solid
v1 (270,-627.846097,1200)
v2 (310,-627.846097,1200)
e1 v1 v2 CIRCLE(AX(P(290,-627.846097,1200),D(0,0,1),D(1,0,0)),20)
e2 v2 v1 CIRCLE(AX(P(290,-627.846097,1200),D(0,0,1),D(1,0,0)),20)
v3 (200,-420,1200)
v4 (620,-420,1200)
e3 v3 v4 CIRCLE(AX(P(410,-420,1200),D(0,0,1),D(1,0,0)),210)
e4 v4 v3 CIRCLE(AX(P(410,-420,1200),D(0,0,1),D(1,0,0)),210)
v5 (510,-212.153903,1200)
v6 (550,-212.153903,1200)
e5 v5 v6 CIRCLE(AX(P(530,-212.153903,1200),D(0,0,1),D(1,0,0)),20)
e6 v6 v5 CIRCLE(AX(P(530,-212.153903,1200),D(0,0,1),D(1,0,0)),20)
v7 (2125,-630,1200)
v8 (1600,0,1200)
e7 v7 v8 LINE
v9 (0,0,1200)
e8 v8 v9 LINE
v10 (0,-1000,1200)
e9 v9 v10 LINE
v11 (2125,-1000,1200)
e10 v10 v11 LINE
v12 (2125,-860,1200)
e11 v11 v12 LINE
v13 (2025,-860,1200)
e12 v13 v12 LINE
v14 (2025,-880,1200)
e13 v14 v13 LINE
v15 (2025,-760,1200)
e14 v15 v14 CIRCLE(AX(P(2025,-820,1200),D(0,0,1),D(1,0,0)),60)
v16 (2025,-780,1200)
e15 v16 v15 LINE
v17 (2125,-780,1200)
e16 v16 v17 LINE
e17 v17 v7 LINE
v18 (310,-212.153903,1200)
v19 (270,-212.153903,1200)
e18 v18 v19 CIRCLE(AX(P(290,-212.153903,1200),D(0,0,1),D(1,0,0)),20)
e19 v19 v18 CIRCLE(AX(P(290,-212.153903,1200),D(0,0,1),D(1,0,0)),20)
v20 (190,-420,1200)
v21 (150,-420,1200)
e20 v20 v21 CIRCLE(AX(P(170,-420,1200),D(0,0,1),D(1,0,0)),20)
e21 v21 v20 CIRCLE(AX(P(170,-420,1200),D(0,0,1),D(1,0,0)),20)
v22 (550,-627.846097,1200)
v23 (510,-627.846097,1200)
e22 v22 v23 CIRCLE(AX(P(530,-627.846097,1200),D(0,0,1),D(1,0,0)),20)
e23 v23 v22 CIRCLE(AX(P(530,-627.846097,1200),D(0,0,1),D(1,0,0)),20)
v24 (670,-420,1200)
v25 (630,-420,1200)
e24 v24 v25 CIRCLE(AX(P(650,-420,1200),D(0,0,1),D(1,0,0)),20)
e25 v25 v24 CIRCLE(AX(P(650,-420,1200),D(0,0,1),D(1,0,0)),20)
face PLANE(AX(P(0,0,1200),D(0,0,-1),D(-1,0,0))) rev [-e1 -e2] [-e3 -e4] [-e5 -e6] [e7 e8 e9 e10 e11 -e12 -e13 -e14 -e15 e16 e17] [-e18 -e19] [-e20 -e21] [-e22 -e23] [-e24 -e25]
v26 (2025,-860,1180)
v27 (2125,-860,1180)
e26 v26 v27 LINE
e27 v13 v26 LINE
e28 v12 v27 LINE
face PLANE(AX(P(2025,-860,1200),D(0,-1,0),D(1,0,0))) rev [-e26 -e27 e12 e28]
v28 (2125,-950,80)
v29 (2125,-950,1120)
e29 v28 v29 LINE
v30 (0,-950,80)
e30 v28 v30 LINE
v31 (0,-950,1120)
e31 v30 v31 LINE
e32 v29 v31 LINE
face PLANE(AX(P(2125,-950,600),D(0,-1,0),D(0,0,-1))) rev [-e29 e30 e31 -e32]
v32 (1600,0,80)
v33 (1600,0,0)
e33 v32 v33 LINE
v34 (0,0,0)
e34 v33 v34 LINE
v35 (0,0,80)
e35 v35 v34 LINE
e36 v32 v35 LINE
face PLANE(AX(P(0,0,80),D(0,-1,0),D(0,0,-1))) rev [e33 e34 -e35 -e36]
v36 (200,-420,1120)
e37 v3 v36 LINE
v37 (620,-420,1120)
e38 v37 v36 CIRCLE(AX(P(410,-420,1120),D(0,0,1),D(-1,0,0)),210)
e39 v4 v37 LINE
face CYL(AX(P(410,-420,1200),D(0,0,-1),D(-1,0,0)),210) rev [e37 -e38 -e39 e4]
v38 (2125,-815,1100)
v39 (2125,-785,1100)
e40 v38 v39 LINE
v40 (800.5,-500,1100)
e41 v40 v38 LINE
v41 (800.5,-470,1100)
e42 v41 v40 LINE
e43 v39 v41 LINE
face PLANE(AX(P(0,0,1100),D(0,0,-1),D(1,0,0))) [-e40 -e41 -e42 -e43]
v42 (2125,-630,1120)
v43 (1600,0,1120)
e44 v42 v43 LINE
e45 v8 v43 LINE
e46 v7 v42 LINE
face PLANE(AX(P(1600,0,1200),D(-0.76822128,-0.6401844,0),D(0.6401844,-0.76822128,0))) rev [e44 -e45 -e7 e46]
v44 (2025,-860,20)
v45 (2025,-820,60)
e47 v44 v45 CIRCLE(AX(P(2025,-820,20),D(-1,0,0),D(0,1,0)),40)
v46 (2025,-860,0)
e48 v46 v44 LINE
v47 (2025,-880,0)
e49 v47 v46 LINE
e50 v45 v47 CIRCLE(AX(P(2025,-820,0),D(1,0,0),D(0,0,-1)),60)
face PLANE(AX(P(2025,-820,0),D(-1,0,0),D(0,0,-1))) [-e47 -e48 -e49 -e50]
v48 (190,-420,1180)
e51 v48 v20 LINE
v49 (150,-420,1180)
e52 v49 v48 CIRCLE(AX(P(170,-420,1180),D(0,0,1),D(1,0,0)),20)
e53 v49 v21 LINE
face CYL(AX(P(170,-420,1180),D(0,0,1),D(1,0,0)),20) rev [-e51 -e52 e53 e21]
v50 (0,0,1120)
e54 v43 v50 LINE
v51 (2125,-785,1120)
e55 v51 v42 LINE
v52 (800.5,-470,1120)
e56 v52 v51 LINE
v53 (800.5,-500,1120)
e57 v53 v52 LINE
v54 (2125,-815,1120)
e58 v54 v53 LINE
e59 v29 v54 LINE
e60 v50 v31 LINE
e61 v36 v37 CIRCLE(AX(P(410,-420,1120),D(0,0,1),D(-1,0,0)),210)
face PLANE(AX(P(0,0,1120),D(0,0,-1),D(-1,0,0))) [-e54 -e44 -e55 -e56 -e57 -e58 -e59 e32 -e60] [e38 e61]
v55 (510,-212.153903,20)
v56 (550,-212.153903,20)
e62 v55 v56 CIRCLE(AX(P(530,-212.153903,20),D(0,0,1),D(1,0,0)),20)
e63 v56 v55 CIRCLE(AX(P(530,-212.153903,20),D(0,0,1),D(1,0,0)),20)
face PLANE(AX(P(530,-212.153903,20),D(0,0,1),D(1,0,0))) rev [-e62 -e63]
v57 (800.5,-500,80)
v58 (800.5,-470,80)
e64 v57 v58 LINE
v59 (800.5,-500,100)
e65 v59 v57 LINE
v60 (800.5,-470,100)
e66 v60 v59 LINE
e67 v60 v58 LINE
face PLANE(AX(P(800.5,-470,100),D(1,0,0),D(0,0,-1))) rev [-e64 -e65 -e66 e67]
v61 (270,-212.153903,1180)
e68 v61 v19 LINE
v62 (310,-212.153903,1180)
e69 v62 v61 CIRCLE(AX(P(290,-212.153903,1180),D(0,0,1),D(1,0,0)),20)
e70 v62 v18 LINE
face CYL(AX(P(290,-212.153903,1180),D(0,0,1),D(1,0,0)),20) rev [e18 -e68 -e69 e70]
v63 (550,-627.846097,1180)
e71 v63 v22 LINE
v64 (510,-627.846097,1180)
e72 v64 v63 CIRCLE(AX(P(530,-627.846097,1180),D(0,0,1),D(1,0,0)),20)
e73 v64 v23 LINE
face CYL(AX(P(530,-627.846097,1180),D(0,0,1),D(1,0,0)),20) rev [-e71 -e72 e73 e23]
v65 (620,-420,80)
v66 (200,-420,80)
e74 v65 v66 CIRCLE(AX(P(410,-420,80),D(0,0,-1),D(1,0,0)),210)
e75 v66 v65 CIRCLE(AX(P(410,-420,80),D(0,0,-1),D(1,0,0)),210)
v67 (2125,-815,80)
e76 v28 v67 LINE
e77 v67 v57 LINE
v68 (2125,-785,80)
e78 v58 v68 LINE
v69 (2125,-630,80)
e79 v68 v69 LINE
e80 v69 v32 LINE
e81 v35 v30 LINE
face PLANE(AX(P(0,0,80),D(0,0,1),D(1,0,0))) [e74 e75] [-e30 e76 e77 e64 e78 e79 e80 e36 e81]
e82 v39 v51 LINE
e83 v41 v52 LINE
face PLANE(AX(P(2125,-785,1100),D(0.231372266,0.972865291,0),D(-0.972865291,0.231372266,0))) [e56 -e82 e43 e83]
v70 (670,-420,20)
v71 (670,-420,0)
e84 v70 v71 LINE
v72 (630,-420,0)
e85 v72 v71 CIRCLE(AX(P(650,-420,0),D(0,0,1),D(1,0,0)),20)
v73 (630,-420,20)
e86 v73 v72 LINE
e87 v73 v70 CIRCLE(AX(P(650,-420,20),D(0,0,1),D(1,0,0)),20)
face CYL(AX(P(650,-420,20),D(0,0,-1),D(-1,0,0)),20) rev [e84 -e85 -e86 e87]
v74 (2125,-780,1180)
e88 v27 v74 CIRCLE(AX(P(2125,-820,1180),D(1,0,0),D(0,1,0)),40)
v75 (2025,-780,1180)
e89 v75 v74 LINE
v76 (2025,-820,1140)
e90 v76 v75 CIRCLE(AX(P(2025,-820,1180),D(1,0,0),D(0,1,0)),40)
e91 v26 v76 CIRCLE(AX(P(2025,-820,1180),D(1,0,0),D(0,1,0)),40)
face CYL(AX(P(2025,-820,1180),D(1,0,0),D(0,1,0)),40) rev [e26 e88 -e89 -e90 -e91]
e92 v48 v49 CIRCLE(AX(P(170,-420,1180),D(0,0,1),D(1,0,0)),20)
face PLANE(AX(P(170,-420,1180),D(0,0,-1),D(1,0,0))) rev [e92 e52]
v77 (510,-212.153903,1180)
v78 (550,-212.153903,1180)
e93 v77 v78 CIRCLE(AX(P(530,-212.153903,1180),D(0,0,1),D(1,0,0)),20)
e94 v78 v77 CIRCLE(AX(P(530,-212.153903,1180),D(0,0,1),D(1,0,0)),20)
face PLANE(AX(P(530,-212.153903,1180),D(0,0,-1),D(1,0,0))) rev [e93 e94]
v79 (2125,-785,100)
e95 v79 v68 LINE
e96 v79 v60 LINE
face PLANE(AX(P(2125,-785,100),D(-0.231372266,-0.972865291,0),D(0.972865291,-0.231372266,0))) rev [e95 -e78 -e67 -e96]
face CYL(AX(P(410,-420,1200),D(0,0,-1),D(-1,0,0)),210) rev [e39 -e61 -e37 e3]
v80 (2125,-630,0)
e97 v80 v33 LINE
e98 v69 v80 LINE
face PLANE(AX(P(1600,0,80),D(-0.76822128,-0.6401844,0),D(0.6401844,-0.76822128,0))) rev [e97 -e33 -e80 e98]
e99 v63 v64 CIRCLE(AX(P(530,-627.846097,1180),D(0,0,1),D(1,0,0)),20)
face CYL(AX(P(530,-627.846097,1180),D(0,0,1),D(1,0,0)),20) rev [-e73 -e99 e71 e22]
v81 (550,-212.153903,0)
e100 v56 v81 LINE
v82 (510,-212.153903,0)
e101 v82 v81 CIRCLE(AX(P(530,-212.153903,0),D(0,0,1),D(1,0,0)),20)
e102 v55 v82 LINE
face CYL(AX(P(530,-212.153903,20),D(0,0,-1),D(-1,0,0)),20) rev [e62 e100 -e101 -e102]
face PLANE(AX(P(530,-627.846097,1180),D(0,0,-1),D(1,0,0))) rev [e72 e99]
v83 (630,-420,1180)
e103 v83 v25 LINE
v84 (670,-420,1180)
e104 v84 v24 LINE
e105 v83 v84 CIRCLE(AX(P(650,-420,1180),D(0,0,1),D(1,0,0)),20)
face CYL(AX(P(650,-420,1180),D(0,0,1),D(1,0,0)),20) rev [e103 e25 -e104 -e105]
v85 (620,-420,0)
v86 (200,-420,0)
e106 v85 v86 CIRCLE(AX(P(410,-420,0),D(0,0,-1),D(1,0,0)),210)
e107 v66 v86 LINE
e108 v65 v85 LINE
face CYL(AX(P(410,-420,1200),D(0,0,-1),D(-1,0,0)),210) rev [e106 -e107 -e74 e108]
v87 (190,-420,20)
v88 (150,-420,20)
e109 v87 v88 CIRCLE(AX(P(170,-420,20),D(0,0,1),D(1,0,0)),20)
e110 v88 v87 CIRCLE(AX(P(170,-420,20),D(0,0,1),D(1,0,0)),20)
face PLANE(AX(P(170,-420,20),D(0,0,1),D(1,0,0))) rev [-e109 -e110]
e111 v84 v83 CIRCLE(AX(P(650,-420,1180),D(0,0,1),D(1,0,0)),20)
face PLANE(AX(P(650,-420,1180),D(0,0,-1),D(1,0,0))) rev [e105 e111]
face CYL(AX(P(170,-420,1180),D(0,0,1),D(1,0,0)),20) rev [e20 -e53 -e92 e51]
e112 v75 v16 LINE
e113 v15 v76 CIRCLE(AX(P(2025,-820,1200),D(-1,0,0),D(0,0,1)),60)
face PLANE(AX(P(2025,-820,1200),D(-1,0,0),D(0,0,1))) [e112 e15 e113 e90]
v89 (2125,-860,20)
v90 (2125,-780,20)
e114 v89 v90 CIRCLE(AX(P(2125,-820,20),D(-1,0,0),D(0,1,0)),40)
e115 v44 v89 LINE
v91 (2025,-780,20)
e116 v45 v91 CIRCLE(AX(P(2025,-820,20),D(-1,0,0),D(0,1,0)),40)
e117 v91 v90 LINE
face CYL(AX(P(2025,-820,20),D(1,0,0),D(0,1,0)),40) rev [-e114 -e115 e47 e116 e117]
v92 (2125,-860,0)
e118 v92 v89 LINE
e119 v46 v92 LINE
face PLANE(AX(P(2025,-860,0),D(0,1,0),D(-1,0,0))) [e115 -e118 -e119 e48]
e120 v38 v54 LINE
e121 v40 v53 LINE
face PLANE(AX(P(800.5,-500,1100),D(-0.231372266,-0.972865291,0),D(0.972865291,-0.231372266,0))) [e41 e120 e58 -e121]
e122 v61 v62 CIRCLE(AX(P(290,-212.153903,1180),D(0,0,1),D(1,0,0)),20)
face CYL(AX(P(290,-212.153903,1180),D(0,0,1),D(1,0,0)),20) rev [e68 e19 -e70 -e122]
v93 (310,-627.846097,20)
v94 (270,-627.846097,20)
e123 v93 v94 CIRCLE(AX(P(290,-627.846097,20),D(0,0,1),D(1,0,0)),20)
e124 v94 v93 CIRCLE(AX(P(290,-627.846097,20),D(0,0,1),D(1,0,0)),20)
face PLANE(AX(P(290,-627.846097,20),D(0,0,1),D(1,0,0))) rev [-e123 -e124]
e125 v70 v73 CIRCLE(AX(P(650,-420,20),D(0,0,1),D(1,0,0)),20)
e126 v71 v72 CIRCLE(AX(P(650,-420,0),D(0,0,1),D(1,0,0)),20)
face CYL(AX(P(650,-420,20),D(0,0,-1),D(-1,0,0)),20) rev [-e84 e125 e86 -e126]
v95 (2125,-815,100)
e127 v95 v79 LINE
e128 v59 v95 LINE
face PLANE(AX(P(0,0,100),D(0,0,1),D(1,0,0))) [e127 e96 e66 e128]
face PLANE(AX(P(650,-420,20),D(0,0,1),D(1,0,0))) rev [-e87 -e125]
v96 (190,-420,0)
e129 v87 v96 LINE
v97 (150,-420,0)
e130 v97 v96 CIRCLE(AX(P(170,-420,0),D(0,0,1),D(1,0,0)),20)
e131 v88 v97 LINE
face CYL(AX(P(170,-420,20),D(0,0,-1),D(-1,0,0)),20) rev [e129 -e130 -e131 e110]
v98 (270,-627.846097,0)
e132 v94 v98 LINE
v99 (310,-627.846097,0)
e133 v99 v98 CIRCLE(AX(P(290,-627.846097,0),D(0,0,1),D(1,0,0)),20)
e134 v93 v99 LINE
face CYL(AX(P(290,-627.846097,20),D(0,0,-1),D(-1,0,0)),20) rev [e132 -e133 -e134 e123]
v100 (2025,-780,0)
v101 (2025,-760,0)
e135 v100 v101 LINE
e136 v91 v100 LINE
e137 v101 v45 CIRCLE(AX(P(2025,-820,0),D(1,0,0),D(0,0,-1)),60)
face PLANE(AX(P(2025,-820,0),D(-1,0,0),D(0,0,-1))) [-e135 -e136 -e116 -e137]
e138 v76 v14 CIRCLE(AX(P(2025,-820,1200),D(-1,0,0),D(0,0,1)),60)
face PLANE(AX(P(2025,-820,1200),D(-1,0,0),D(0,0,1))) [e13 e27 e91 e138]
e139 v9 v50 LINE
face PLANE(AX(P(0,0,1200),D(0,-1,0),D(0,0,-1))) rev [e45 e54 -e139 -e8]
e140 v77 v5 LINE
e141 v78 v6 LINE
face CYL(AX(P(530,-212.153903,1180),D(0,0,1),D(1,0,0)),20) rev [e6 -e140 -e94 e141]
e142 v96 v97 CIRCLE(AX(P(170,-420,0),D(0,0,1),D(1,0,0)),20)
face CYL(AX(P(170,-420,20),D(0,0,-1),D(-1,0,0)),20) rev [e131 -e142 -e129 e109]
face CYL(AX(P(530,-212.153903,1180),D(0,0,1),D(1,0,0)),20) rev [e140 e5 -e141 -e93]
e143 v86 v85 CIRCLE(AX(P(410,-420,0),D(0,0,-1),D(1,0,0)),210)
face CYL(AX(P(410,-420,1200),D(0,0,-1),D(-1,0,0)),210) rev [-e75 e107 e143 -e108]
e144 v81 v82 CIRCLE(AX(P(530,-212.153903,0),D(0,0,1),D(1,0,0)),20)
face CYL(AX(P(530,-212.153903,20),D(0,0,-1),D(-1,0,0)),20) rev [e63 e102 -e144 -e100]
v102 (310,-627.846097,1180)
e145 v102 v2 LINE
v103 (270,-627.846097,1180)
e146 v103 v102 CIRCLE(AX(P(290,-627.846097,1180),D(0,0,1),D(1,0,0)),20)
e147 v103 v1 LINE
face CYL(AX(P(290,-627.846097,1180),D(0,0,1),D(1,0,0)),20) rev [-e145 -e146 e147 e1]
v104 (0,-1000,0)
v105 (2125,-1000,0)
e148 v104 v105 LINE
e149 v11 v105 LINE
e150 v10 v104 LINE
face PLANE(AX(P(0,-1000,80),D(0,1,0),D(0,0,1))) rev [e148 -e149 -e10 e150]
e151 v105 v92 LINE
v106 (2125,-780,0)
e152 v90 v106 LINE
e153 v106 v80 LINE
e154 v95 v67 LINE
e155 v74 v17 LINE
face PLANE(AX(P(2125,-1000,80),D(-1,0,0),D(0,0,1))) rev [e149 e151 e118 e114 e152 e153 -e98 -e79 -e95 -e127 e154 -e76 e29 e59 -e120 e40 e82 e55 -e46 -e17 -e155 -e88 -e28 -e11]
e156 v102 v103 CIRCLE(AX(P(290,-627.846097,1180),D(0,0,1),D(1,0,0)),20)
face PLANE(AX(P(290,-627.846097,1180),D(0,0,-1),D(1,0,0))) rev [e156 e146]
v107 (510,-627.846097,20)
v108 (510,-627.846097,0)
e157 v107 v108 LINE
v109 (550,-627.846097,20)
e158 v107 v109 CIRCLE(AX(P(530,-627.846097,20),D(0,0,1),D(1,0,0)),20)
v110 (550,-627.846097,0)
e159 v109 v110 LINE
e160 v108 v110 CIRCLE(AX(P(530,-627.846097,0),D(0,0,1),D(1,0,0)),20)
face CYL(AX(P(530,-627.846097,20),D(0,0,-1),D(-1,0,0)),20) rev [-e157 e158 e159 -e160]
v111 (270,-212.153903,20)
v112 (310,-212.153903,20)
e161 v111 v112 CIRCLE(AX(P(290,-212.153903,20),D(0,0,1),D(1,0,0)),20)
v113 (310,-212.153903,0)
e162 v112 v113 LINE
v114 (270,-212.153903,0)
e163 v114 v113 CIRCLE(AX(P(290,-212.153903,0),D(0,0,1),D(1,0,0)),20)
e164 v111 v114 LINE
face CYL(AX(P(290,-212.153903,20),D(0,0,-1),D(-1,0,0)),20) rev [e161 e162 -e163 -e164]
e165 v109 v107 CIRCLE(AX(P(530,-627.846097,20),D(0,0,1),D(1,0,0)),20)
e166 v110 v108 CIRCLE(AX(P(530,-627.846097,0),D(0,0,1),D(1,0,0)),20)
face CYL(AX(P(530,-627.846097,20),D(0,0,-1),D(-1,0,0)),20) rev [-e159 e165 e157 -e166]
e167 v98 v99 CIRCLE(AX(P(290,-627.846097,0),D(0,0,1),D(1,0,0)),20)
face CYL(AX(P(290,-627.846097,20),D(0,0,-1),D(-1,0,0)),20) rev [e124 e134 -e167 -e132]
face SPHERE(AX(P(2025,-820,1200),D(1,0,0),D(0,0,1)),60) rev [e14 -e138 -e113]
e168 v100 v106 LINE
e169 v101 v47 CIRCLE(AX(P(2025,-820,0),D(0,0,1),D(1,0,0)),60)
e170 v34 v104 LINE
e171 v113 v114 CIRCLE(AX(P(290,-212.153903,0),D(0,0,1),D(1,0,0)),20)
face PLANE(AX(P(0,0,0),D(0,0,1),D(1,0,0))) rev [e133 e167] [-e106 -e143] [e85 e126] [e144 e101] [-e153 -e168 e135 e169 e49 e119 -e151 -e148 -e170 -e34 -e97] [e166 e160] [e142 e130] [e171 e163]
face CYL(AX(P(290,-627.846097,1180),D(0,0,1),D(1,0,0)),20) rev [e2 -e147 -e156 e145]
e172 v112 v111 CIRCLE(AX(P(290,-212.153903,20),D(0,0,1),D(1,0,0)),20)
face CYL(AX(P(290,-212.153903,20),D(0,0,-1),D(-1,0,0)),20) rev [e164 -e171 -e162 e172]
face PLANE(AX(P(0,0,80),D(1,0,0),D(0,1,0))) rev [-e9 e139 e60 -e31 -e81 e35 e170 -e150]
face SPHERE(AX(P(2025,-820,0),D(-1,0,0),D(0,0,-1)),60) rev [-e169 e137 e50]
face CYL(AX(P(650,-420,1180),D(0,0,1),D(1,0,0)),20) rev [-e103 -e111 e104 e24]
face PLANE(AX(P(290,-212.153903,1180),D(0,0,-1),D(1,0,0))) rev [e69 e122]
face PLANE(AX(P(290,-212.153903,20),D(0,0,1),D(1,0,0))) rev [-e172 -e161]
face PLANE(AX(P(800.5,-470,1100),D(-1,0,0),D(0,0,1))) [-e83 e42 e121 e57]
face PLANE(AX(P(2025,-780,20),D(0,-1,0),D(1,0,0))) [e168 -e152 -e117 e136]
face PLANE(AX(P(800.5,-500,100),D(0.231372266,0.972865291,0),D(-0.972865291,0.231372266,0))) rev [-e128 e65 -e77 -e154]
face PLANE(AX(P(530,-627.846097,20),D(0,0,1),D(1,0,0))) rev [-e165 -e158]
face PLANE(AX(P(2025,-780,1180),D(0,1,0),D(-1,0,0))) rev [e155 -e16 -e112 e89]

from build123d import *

# Parameters (mm, degrees)
EXTRUDE_1_DEPTH          = 80
SKETCH_4_W               = 520
SKETCH_4_H               = 50
EXTRUDE_2_DEPTH          = 2125
EXTRUDE_3_DEPTH          = 80
CUT_EXTRUDE_3_DEPTH      = 2638.351891576
CUT_EXTRUDE_3_DEPTH_BACK = 2638.351891576
SKETCH_2_R               = 210
EXTRUDE_4_DEPTH          = 100
SKETCH_7_R               = 20
CUT_EXTRUDE_5_DEPTH      = 20
CUT_EXTRUDE_6_DEPTH      = 100
CUT_REVOLVE_1_ANGLE      = 90


with BuildPart() as part:
    # 草图1 → 凸台-拉伸1 (new body)
    with BuildSketch(Plane.XY):
        Polygon((0, 0), (0, -1000), (2125, -1000), (2125, -630), (1600, 0), align=None)
    extrude(amount=EXTRUDE_1_DEPTH)

    # 草图4 → 凸台-拉伸2 (add)
    with BuildSketch(Plane(origin=(0, 0, 0), x_dir=(0, 0, -1), z_dir=(1, 0, 0))):
        with Locations((-340, -975)):
            Rectangle(SKETCH_4_W, SKETCH_4_H)
    extrude_2 = extrude(amount=EXTRUDE_2_DEPTH)

    # 镜向4: 凸台-拉伸2 across plane
    add(extrude_2.mirror(Plane.XY.offset(600)))

    # 草图5 → 凸台-拉伸3 (add)
    with BuildSketch(Plane.XY.offset(1120)):
        Polygon((0, -1000), (0, 0), (1600, 0), (2125, -630), (2125, -1000), align=None)
    extrude(amount=EXTRUDE_3_DEPTH)

    # 草图2 → 切除-拉伸3 (cut, two sides: drawn at the far end of the back side and taken through both)
    with BuildSketch(Plane.XY.offset(-CUT_EXTRUDE_3_DEPTH_BACK)):
        with Locations(Location((410, -420, 0), (0, 0, 180))):
            Circle(SKETCH_2_R)
    extrude(amount=CUT_EXTRUDE_3_DEPTH + CUT_EXTRUDE_3_DEPTH_BACK, mode=Mode.SUBTRACT)

    # 草图6 → 凸台-拉伸4 (add)
    with BuildSketch(Plane.XY):
        Polygon((800.5, -500), (2125, -815), (2125, -785), (800.5, -470), align=None)
    extrude_4 = extrude(amount=EXTRUDE_4_DEPTH)

    # 镜向5: 凸台-拉伸4 across plane
    add(extrude_4.mirror(Plane.XY.offset(600)))

    # 草图7 → 切除-拉伸5 (cut)
    with BuildSketch(Plane.XY):
        with Locations((170, -420)):
            Circle(SKETCH_7_R)
        with Locations((289.999999999, -627.846096908)):
            Circle(SKETCH_7_R)
        with Locations((530.000000001, -627.846096908)):
            Circle(SKETCH_7_R)
        with Locations((650, -420)):
            Circle(SKETCH_7_R)
        with Locations((289.999999999, -212.153903092)):
            Circle(SKETCH_7_R)
        with Locations((530.000000001, -212.153903092)):
            Circle(SKETCH_7_R)
    cut_extrude_5 = extrude(amount=CUT_EXTRUDE_5_DEPTH, mode=Mode.SUBTRACT)

    # 镜向6: 切除-拉伸5 across plane
    add(cut_extrude_5.mirror(Plane.XY.offset(600)), mode=Mode.SUBTRACT)

    # 草图8 → 切除-拉伸6 (cut)
    with BuildSketch(Plane(origin=(2125, 0, 0), x_dir=(0, 0, -1), z_dir=(1, 0, 0))):
        with BuildLine():
            Line((-1200, -860), (-1180, -860))
            ThreePointArc((-1180, -860), (-1140, -820), (-1180, -780))
            Line((-1180, -780), (-1200, -780))
            Line((-1200, -780), (-1200, -860))
        make_face()
    cut_extrude_6 = extrude(amount=-CUT_EXTRUDE_6_DEPTH, mode=Mode.SUBTRACT)

    # 草图9 → 切除-旋转1 (revolve, cut)
    with BuildSketch(Plane.XY.offset(1200)):
        with BuildLine():
            Line((2025, -760), (2025, -880))
            ThreePointArc((2025, -880), (1965, -820), (2025, -760))
        make_face()
    cut_revolve_1 = revolve(axis=Axis((2025, -760, 1200), (0, -1, 0)), revolution_arc=CUT_REVOLVE_1_ANGLE, mode=Mode.SUBTRACT)

    # 镜向7: 切除-拉伸6, 切除-旋转1 across plane
    add(cut_extrude_6.mirror(Plane.XY.offset(600)), mode=Mode.SUBTRACT)
    add(cut_revolve_1.mirror(Plane.XY.offset(600)), mode=Mode.SUBTRACT)


solid = part.part
